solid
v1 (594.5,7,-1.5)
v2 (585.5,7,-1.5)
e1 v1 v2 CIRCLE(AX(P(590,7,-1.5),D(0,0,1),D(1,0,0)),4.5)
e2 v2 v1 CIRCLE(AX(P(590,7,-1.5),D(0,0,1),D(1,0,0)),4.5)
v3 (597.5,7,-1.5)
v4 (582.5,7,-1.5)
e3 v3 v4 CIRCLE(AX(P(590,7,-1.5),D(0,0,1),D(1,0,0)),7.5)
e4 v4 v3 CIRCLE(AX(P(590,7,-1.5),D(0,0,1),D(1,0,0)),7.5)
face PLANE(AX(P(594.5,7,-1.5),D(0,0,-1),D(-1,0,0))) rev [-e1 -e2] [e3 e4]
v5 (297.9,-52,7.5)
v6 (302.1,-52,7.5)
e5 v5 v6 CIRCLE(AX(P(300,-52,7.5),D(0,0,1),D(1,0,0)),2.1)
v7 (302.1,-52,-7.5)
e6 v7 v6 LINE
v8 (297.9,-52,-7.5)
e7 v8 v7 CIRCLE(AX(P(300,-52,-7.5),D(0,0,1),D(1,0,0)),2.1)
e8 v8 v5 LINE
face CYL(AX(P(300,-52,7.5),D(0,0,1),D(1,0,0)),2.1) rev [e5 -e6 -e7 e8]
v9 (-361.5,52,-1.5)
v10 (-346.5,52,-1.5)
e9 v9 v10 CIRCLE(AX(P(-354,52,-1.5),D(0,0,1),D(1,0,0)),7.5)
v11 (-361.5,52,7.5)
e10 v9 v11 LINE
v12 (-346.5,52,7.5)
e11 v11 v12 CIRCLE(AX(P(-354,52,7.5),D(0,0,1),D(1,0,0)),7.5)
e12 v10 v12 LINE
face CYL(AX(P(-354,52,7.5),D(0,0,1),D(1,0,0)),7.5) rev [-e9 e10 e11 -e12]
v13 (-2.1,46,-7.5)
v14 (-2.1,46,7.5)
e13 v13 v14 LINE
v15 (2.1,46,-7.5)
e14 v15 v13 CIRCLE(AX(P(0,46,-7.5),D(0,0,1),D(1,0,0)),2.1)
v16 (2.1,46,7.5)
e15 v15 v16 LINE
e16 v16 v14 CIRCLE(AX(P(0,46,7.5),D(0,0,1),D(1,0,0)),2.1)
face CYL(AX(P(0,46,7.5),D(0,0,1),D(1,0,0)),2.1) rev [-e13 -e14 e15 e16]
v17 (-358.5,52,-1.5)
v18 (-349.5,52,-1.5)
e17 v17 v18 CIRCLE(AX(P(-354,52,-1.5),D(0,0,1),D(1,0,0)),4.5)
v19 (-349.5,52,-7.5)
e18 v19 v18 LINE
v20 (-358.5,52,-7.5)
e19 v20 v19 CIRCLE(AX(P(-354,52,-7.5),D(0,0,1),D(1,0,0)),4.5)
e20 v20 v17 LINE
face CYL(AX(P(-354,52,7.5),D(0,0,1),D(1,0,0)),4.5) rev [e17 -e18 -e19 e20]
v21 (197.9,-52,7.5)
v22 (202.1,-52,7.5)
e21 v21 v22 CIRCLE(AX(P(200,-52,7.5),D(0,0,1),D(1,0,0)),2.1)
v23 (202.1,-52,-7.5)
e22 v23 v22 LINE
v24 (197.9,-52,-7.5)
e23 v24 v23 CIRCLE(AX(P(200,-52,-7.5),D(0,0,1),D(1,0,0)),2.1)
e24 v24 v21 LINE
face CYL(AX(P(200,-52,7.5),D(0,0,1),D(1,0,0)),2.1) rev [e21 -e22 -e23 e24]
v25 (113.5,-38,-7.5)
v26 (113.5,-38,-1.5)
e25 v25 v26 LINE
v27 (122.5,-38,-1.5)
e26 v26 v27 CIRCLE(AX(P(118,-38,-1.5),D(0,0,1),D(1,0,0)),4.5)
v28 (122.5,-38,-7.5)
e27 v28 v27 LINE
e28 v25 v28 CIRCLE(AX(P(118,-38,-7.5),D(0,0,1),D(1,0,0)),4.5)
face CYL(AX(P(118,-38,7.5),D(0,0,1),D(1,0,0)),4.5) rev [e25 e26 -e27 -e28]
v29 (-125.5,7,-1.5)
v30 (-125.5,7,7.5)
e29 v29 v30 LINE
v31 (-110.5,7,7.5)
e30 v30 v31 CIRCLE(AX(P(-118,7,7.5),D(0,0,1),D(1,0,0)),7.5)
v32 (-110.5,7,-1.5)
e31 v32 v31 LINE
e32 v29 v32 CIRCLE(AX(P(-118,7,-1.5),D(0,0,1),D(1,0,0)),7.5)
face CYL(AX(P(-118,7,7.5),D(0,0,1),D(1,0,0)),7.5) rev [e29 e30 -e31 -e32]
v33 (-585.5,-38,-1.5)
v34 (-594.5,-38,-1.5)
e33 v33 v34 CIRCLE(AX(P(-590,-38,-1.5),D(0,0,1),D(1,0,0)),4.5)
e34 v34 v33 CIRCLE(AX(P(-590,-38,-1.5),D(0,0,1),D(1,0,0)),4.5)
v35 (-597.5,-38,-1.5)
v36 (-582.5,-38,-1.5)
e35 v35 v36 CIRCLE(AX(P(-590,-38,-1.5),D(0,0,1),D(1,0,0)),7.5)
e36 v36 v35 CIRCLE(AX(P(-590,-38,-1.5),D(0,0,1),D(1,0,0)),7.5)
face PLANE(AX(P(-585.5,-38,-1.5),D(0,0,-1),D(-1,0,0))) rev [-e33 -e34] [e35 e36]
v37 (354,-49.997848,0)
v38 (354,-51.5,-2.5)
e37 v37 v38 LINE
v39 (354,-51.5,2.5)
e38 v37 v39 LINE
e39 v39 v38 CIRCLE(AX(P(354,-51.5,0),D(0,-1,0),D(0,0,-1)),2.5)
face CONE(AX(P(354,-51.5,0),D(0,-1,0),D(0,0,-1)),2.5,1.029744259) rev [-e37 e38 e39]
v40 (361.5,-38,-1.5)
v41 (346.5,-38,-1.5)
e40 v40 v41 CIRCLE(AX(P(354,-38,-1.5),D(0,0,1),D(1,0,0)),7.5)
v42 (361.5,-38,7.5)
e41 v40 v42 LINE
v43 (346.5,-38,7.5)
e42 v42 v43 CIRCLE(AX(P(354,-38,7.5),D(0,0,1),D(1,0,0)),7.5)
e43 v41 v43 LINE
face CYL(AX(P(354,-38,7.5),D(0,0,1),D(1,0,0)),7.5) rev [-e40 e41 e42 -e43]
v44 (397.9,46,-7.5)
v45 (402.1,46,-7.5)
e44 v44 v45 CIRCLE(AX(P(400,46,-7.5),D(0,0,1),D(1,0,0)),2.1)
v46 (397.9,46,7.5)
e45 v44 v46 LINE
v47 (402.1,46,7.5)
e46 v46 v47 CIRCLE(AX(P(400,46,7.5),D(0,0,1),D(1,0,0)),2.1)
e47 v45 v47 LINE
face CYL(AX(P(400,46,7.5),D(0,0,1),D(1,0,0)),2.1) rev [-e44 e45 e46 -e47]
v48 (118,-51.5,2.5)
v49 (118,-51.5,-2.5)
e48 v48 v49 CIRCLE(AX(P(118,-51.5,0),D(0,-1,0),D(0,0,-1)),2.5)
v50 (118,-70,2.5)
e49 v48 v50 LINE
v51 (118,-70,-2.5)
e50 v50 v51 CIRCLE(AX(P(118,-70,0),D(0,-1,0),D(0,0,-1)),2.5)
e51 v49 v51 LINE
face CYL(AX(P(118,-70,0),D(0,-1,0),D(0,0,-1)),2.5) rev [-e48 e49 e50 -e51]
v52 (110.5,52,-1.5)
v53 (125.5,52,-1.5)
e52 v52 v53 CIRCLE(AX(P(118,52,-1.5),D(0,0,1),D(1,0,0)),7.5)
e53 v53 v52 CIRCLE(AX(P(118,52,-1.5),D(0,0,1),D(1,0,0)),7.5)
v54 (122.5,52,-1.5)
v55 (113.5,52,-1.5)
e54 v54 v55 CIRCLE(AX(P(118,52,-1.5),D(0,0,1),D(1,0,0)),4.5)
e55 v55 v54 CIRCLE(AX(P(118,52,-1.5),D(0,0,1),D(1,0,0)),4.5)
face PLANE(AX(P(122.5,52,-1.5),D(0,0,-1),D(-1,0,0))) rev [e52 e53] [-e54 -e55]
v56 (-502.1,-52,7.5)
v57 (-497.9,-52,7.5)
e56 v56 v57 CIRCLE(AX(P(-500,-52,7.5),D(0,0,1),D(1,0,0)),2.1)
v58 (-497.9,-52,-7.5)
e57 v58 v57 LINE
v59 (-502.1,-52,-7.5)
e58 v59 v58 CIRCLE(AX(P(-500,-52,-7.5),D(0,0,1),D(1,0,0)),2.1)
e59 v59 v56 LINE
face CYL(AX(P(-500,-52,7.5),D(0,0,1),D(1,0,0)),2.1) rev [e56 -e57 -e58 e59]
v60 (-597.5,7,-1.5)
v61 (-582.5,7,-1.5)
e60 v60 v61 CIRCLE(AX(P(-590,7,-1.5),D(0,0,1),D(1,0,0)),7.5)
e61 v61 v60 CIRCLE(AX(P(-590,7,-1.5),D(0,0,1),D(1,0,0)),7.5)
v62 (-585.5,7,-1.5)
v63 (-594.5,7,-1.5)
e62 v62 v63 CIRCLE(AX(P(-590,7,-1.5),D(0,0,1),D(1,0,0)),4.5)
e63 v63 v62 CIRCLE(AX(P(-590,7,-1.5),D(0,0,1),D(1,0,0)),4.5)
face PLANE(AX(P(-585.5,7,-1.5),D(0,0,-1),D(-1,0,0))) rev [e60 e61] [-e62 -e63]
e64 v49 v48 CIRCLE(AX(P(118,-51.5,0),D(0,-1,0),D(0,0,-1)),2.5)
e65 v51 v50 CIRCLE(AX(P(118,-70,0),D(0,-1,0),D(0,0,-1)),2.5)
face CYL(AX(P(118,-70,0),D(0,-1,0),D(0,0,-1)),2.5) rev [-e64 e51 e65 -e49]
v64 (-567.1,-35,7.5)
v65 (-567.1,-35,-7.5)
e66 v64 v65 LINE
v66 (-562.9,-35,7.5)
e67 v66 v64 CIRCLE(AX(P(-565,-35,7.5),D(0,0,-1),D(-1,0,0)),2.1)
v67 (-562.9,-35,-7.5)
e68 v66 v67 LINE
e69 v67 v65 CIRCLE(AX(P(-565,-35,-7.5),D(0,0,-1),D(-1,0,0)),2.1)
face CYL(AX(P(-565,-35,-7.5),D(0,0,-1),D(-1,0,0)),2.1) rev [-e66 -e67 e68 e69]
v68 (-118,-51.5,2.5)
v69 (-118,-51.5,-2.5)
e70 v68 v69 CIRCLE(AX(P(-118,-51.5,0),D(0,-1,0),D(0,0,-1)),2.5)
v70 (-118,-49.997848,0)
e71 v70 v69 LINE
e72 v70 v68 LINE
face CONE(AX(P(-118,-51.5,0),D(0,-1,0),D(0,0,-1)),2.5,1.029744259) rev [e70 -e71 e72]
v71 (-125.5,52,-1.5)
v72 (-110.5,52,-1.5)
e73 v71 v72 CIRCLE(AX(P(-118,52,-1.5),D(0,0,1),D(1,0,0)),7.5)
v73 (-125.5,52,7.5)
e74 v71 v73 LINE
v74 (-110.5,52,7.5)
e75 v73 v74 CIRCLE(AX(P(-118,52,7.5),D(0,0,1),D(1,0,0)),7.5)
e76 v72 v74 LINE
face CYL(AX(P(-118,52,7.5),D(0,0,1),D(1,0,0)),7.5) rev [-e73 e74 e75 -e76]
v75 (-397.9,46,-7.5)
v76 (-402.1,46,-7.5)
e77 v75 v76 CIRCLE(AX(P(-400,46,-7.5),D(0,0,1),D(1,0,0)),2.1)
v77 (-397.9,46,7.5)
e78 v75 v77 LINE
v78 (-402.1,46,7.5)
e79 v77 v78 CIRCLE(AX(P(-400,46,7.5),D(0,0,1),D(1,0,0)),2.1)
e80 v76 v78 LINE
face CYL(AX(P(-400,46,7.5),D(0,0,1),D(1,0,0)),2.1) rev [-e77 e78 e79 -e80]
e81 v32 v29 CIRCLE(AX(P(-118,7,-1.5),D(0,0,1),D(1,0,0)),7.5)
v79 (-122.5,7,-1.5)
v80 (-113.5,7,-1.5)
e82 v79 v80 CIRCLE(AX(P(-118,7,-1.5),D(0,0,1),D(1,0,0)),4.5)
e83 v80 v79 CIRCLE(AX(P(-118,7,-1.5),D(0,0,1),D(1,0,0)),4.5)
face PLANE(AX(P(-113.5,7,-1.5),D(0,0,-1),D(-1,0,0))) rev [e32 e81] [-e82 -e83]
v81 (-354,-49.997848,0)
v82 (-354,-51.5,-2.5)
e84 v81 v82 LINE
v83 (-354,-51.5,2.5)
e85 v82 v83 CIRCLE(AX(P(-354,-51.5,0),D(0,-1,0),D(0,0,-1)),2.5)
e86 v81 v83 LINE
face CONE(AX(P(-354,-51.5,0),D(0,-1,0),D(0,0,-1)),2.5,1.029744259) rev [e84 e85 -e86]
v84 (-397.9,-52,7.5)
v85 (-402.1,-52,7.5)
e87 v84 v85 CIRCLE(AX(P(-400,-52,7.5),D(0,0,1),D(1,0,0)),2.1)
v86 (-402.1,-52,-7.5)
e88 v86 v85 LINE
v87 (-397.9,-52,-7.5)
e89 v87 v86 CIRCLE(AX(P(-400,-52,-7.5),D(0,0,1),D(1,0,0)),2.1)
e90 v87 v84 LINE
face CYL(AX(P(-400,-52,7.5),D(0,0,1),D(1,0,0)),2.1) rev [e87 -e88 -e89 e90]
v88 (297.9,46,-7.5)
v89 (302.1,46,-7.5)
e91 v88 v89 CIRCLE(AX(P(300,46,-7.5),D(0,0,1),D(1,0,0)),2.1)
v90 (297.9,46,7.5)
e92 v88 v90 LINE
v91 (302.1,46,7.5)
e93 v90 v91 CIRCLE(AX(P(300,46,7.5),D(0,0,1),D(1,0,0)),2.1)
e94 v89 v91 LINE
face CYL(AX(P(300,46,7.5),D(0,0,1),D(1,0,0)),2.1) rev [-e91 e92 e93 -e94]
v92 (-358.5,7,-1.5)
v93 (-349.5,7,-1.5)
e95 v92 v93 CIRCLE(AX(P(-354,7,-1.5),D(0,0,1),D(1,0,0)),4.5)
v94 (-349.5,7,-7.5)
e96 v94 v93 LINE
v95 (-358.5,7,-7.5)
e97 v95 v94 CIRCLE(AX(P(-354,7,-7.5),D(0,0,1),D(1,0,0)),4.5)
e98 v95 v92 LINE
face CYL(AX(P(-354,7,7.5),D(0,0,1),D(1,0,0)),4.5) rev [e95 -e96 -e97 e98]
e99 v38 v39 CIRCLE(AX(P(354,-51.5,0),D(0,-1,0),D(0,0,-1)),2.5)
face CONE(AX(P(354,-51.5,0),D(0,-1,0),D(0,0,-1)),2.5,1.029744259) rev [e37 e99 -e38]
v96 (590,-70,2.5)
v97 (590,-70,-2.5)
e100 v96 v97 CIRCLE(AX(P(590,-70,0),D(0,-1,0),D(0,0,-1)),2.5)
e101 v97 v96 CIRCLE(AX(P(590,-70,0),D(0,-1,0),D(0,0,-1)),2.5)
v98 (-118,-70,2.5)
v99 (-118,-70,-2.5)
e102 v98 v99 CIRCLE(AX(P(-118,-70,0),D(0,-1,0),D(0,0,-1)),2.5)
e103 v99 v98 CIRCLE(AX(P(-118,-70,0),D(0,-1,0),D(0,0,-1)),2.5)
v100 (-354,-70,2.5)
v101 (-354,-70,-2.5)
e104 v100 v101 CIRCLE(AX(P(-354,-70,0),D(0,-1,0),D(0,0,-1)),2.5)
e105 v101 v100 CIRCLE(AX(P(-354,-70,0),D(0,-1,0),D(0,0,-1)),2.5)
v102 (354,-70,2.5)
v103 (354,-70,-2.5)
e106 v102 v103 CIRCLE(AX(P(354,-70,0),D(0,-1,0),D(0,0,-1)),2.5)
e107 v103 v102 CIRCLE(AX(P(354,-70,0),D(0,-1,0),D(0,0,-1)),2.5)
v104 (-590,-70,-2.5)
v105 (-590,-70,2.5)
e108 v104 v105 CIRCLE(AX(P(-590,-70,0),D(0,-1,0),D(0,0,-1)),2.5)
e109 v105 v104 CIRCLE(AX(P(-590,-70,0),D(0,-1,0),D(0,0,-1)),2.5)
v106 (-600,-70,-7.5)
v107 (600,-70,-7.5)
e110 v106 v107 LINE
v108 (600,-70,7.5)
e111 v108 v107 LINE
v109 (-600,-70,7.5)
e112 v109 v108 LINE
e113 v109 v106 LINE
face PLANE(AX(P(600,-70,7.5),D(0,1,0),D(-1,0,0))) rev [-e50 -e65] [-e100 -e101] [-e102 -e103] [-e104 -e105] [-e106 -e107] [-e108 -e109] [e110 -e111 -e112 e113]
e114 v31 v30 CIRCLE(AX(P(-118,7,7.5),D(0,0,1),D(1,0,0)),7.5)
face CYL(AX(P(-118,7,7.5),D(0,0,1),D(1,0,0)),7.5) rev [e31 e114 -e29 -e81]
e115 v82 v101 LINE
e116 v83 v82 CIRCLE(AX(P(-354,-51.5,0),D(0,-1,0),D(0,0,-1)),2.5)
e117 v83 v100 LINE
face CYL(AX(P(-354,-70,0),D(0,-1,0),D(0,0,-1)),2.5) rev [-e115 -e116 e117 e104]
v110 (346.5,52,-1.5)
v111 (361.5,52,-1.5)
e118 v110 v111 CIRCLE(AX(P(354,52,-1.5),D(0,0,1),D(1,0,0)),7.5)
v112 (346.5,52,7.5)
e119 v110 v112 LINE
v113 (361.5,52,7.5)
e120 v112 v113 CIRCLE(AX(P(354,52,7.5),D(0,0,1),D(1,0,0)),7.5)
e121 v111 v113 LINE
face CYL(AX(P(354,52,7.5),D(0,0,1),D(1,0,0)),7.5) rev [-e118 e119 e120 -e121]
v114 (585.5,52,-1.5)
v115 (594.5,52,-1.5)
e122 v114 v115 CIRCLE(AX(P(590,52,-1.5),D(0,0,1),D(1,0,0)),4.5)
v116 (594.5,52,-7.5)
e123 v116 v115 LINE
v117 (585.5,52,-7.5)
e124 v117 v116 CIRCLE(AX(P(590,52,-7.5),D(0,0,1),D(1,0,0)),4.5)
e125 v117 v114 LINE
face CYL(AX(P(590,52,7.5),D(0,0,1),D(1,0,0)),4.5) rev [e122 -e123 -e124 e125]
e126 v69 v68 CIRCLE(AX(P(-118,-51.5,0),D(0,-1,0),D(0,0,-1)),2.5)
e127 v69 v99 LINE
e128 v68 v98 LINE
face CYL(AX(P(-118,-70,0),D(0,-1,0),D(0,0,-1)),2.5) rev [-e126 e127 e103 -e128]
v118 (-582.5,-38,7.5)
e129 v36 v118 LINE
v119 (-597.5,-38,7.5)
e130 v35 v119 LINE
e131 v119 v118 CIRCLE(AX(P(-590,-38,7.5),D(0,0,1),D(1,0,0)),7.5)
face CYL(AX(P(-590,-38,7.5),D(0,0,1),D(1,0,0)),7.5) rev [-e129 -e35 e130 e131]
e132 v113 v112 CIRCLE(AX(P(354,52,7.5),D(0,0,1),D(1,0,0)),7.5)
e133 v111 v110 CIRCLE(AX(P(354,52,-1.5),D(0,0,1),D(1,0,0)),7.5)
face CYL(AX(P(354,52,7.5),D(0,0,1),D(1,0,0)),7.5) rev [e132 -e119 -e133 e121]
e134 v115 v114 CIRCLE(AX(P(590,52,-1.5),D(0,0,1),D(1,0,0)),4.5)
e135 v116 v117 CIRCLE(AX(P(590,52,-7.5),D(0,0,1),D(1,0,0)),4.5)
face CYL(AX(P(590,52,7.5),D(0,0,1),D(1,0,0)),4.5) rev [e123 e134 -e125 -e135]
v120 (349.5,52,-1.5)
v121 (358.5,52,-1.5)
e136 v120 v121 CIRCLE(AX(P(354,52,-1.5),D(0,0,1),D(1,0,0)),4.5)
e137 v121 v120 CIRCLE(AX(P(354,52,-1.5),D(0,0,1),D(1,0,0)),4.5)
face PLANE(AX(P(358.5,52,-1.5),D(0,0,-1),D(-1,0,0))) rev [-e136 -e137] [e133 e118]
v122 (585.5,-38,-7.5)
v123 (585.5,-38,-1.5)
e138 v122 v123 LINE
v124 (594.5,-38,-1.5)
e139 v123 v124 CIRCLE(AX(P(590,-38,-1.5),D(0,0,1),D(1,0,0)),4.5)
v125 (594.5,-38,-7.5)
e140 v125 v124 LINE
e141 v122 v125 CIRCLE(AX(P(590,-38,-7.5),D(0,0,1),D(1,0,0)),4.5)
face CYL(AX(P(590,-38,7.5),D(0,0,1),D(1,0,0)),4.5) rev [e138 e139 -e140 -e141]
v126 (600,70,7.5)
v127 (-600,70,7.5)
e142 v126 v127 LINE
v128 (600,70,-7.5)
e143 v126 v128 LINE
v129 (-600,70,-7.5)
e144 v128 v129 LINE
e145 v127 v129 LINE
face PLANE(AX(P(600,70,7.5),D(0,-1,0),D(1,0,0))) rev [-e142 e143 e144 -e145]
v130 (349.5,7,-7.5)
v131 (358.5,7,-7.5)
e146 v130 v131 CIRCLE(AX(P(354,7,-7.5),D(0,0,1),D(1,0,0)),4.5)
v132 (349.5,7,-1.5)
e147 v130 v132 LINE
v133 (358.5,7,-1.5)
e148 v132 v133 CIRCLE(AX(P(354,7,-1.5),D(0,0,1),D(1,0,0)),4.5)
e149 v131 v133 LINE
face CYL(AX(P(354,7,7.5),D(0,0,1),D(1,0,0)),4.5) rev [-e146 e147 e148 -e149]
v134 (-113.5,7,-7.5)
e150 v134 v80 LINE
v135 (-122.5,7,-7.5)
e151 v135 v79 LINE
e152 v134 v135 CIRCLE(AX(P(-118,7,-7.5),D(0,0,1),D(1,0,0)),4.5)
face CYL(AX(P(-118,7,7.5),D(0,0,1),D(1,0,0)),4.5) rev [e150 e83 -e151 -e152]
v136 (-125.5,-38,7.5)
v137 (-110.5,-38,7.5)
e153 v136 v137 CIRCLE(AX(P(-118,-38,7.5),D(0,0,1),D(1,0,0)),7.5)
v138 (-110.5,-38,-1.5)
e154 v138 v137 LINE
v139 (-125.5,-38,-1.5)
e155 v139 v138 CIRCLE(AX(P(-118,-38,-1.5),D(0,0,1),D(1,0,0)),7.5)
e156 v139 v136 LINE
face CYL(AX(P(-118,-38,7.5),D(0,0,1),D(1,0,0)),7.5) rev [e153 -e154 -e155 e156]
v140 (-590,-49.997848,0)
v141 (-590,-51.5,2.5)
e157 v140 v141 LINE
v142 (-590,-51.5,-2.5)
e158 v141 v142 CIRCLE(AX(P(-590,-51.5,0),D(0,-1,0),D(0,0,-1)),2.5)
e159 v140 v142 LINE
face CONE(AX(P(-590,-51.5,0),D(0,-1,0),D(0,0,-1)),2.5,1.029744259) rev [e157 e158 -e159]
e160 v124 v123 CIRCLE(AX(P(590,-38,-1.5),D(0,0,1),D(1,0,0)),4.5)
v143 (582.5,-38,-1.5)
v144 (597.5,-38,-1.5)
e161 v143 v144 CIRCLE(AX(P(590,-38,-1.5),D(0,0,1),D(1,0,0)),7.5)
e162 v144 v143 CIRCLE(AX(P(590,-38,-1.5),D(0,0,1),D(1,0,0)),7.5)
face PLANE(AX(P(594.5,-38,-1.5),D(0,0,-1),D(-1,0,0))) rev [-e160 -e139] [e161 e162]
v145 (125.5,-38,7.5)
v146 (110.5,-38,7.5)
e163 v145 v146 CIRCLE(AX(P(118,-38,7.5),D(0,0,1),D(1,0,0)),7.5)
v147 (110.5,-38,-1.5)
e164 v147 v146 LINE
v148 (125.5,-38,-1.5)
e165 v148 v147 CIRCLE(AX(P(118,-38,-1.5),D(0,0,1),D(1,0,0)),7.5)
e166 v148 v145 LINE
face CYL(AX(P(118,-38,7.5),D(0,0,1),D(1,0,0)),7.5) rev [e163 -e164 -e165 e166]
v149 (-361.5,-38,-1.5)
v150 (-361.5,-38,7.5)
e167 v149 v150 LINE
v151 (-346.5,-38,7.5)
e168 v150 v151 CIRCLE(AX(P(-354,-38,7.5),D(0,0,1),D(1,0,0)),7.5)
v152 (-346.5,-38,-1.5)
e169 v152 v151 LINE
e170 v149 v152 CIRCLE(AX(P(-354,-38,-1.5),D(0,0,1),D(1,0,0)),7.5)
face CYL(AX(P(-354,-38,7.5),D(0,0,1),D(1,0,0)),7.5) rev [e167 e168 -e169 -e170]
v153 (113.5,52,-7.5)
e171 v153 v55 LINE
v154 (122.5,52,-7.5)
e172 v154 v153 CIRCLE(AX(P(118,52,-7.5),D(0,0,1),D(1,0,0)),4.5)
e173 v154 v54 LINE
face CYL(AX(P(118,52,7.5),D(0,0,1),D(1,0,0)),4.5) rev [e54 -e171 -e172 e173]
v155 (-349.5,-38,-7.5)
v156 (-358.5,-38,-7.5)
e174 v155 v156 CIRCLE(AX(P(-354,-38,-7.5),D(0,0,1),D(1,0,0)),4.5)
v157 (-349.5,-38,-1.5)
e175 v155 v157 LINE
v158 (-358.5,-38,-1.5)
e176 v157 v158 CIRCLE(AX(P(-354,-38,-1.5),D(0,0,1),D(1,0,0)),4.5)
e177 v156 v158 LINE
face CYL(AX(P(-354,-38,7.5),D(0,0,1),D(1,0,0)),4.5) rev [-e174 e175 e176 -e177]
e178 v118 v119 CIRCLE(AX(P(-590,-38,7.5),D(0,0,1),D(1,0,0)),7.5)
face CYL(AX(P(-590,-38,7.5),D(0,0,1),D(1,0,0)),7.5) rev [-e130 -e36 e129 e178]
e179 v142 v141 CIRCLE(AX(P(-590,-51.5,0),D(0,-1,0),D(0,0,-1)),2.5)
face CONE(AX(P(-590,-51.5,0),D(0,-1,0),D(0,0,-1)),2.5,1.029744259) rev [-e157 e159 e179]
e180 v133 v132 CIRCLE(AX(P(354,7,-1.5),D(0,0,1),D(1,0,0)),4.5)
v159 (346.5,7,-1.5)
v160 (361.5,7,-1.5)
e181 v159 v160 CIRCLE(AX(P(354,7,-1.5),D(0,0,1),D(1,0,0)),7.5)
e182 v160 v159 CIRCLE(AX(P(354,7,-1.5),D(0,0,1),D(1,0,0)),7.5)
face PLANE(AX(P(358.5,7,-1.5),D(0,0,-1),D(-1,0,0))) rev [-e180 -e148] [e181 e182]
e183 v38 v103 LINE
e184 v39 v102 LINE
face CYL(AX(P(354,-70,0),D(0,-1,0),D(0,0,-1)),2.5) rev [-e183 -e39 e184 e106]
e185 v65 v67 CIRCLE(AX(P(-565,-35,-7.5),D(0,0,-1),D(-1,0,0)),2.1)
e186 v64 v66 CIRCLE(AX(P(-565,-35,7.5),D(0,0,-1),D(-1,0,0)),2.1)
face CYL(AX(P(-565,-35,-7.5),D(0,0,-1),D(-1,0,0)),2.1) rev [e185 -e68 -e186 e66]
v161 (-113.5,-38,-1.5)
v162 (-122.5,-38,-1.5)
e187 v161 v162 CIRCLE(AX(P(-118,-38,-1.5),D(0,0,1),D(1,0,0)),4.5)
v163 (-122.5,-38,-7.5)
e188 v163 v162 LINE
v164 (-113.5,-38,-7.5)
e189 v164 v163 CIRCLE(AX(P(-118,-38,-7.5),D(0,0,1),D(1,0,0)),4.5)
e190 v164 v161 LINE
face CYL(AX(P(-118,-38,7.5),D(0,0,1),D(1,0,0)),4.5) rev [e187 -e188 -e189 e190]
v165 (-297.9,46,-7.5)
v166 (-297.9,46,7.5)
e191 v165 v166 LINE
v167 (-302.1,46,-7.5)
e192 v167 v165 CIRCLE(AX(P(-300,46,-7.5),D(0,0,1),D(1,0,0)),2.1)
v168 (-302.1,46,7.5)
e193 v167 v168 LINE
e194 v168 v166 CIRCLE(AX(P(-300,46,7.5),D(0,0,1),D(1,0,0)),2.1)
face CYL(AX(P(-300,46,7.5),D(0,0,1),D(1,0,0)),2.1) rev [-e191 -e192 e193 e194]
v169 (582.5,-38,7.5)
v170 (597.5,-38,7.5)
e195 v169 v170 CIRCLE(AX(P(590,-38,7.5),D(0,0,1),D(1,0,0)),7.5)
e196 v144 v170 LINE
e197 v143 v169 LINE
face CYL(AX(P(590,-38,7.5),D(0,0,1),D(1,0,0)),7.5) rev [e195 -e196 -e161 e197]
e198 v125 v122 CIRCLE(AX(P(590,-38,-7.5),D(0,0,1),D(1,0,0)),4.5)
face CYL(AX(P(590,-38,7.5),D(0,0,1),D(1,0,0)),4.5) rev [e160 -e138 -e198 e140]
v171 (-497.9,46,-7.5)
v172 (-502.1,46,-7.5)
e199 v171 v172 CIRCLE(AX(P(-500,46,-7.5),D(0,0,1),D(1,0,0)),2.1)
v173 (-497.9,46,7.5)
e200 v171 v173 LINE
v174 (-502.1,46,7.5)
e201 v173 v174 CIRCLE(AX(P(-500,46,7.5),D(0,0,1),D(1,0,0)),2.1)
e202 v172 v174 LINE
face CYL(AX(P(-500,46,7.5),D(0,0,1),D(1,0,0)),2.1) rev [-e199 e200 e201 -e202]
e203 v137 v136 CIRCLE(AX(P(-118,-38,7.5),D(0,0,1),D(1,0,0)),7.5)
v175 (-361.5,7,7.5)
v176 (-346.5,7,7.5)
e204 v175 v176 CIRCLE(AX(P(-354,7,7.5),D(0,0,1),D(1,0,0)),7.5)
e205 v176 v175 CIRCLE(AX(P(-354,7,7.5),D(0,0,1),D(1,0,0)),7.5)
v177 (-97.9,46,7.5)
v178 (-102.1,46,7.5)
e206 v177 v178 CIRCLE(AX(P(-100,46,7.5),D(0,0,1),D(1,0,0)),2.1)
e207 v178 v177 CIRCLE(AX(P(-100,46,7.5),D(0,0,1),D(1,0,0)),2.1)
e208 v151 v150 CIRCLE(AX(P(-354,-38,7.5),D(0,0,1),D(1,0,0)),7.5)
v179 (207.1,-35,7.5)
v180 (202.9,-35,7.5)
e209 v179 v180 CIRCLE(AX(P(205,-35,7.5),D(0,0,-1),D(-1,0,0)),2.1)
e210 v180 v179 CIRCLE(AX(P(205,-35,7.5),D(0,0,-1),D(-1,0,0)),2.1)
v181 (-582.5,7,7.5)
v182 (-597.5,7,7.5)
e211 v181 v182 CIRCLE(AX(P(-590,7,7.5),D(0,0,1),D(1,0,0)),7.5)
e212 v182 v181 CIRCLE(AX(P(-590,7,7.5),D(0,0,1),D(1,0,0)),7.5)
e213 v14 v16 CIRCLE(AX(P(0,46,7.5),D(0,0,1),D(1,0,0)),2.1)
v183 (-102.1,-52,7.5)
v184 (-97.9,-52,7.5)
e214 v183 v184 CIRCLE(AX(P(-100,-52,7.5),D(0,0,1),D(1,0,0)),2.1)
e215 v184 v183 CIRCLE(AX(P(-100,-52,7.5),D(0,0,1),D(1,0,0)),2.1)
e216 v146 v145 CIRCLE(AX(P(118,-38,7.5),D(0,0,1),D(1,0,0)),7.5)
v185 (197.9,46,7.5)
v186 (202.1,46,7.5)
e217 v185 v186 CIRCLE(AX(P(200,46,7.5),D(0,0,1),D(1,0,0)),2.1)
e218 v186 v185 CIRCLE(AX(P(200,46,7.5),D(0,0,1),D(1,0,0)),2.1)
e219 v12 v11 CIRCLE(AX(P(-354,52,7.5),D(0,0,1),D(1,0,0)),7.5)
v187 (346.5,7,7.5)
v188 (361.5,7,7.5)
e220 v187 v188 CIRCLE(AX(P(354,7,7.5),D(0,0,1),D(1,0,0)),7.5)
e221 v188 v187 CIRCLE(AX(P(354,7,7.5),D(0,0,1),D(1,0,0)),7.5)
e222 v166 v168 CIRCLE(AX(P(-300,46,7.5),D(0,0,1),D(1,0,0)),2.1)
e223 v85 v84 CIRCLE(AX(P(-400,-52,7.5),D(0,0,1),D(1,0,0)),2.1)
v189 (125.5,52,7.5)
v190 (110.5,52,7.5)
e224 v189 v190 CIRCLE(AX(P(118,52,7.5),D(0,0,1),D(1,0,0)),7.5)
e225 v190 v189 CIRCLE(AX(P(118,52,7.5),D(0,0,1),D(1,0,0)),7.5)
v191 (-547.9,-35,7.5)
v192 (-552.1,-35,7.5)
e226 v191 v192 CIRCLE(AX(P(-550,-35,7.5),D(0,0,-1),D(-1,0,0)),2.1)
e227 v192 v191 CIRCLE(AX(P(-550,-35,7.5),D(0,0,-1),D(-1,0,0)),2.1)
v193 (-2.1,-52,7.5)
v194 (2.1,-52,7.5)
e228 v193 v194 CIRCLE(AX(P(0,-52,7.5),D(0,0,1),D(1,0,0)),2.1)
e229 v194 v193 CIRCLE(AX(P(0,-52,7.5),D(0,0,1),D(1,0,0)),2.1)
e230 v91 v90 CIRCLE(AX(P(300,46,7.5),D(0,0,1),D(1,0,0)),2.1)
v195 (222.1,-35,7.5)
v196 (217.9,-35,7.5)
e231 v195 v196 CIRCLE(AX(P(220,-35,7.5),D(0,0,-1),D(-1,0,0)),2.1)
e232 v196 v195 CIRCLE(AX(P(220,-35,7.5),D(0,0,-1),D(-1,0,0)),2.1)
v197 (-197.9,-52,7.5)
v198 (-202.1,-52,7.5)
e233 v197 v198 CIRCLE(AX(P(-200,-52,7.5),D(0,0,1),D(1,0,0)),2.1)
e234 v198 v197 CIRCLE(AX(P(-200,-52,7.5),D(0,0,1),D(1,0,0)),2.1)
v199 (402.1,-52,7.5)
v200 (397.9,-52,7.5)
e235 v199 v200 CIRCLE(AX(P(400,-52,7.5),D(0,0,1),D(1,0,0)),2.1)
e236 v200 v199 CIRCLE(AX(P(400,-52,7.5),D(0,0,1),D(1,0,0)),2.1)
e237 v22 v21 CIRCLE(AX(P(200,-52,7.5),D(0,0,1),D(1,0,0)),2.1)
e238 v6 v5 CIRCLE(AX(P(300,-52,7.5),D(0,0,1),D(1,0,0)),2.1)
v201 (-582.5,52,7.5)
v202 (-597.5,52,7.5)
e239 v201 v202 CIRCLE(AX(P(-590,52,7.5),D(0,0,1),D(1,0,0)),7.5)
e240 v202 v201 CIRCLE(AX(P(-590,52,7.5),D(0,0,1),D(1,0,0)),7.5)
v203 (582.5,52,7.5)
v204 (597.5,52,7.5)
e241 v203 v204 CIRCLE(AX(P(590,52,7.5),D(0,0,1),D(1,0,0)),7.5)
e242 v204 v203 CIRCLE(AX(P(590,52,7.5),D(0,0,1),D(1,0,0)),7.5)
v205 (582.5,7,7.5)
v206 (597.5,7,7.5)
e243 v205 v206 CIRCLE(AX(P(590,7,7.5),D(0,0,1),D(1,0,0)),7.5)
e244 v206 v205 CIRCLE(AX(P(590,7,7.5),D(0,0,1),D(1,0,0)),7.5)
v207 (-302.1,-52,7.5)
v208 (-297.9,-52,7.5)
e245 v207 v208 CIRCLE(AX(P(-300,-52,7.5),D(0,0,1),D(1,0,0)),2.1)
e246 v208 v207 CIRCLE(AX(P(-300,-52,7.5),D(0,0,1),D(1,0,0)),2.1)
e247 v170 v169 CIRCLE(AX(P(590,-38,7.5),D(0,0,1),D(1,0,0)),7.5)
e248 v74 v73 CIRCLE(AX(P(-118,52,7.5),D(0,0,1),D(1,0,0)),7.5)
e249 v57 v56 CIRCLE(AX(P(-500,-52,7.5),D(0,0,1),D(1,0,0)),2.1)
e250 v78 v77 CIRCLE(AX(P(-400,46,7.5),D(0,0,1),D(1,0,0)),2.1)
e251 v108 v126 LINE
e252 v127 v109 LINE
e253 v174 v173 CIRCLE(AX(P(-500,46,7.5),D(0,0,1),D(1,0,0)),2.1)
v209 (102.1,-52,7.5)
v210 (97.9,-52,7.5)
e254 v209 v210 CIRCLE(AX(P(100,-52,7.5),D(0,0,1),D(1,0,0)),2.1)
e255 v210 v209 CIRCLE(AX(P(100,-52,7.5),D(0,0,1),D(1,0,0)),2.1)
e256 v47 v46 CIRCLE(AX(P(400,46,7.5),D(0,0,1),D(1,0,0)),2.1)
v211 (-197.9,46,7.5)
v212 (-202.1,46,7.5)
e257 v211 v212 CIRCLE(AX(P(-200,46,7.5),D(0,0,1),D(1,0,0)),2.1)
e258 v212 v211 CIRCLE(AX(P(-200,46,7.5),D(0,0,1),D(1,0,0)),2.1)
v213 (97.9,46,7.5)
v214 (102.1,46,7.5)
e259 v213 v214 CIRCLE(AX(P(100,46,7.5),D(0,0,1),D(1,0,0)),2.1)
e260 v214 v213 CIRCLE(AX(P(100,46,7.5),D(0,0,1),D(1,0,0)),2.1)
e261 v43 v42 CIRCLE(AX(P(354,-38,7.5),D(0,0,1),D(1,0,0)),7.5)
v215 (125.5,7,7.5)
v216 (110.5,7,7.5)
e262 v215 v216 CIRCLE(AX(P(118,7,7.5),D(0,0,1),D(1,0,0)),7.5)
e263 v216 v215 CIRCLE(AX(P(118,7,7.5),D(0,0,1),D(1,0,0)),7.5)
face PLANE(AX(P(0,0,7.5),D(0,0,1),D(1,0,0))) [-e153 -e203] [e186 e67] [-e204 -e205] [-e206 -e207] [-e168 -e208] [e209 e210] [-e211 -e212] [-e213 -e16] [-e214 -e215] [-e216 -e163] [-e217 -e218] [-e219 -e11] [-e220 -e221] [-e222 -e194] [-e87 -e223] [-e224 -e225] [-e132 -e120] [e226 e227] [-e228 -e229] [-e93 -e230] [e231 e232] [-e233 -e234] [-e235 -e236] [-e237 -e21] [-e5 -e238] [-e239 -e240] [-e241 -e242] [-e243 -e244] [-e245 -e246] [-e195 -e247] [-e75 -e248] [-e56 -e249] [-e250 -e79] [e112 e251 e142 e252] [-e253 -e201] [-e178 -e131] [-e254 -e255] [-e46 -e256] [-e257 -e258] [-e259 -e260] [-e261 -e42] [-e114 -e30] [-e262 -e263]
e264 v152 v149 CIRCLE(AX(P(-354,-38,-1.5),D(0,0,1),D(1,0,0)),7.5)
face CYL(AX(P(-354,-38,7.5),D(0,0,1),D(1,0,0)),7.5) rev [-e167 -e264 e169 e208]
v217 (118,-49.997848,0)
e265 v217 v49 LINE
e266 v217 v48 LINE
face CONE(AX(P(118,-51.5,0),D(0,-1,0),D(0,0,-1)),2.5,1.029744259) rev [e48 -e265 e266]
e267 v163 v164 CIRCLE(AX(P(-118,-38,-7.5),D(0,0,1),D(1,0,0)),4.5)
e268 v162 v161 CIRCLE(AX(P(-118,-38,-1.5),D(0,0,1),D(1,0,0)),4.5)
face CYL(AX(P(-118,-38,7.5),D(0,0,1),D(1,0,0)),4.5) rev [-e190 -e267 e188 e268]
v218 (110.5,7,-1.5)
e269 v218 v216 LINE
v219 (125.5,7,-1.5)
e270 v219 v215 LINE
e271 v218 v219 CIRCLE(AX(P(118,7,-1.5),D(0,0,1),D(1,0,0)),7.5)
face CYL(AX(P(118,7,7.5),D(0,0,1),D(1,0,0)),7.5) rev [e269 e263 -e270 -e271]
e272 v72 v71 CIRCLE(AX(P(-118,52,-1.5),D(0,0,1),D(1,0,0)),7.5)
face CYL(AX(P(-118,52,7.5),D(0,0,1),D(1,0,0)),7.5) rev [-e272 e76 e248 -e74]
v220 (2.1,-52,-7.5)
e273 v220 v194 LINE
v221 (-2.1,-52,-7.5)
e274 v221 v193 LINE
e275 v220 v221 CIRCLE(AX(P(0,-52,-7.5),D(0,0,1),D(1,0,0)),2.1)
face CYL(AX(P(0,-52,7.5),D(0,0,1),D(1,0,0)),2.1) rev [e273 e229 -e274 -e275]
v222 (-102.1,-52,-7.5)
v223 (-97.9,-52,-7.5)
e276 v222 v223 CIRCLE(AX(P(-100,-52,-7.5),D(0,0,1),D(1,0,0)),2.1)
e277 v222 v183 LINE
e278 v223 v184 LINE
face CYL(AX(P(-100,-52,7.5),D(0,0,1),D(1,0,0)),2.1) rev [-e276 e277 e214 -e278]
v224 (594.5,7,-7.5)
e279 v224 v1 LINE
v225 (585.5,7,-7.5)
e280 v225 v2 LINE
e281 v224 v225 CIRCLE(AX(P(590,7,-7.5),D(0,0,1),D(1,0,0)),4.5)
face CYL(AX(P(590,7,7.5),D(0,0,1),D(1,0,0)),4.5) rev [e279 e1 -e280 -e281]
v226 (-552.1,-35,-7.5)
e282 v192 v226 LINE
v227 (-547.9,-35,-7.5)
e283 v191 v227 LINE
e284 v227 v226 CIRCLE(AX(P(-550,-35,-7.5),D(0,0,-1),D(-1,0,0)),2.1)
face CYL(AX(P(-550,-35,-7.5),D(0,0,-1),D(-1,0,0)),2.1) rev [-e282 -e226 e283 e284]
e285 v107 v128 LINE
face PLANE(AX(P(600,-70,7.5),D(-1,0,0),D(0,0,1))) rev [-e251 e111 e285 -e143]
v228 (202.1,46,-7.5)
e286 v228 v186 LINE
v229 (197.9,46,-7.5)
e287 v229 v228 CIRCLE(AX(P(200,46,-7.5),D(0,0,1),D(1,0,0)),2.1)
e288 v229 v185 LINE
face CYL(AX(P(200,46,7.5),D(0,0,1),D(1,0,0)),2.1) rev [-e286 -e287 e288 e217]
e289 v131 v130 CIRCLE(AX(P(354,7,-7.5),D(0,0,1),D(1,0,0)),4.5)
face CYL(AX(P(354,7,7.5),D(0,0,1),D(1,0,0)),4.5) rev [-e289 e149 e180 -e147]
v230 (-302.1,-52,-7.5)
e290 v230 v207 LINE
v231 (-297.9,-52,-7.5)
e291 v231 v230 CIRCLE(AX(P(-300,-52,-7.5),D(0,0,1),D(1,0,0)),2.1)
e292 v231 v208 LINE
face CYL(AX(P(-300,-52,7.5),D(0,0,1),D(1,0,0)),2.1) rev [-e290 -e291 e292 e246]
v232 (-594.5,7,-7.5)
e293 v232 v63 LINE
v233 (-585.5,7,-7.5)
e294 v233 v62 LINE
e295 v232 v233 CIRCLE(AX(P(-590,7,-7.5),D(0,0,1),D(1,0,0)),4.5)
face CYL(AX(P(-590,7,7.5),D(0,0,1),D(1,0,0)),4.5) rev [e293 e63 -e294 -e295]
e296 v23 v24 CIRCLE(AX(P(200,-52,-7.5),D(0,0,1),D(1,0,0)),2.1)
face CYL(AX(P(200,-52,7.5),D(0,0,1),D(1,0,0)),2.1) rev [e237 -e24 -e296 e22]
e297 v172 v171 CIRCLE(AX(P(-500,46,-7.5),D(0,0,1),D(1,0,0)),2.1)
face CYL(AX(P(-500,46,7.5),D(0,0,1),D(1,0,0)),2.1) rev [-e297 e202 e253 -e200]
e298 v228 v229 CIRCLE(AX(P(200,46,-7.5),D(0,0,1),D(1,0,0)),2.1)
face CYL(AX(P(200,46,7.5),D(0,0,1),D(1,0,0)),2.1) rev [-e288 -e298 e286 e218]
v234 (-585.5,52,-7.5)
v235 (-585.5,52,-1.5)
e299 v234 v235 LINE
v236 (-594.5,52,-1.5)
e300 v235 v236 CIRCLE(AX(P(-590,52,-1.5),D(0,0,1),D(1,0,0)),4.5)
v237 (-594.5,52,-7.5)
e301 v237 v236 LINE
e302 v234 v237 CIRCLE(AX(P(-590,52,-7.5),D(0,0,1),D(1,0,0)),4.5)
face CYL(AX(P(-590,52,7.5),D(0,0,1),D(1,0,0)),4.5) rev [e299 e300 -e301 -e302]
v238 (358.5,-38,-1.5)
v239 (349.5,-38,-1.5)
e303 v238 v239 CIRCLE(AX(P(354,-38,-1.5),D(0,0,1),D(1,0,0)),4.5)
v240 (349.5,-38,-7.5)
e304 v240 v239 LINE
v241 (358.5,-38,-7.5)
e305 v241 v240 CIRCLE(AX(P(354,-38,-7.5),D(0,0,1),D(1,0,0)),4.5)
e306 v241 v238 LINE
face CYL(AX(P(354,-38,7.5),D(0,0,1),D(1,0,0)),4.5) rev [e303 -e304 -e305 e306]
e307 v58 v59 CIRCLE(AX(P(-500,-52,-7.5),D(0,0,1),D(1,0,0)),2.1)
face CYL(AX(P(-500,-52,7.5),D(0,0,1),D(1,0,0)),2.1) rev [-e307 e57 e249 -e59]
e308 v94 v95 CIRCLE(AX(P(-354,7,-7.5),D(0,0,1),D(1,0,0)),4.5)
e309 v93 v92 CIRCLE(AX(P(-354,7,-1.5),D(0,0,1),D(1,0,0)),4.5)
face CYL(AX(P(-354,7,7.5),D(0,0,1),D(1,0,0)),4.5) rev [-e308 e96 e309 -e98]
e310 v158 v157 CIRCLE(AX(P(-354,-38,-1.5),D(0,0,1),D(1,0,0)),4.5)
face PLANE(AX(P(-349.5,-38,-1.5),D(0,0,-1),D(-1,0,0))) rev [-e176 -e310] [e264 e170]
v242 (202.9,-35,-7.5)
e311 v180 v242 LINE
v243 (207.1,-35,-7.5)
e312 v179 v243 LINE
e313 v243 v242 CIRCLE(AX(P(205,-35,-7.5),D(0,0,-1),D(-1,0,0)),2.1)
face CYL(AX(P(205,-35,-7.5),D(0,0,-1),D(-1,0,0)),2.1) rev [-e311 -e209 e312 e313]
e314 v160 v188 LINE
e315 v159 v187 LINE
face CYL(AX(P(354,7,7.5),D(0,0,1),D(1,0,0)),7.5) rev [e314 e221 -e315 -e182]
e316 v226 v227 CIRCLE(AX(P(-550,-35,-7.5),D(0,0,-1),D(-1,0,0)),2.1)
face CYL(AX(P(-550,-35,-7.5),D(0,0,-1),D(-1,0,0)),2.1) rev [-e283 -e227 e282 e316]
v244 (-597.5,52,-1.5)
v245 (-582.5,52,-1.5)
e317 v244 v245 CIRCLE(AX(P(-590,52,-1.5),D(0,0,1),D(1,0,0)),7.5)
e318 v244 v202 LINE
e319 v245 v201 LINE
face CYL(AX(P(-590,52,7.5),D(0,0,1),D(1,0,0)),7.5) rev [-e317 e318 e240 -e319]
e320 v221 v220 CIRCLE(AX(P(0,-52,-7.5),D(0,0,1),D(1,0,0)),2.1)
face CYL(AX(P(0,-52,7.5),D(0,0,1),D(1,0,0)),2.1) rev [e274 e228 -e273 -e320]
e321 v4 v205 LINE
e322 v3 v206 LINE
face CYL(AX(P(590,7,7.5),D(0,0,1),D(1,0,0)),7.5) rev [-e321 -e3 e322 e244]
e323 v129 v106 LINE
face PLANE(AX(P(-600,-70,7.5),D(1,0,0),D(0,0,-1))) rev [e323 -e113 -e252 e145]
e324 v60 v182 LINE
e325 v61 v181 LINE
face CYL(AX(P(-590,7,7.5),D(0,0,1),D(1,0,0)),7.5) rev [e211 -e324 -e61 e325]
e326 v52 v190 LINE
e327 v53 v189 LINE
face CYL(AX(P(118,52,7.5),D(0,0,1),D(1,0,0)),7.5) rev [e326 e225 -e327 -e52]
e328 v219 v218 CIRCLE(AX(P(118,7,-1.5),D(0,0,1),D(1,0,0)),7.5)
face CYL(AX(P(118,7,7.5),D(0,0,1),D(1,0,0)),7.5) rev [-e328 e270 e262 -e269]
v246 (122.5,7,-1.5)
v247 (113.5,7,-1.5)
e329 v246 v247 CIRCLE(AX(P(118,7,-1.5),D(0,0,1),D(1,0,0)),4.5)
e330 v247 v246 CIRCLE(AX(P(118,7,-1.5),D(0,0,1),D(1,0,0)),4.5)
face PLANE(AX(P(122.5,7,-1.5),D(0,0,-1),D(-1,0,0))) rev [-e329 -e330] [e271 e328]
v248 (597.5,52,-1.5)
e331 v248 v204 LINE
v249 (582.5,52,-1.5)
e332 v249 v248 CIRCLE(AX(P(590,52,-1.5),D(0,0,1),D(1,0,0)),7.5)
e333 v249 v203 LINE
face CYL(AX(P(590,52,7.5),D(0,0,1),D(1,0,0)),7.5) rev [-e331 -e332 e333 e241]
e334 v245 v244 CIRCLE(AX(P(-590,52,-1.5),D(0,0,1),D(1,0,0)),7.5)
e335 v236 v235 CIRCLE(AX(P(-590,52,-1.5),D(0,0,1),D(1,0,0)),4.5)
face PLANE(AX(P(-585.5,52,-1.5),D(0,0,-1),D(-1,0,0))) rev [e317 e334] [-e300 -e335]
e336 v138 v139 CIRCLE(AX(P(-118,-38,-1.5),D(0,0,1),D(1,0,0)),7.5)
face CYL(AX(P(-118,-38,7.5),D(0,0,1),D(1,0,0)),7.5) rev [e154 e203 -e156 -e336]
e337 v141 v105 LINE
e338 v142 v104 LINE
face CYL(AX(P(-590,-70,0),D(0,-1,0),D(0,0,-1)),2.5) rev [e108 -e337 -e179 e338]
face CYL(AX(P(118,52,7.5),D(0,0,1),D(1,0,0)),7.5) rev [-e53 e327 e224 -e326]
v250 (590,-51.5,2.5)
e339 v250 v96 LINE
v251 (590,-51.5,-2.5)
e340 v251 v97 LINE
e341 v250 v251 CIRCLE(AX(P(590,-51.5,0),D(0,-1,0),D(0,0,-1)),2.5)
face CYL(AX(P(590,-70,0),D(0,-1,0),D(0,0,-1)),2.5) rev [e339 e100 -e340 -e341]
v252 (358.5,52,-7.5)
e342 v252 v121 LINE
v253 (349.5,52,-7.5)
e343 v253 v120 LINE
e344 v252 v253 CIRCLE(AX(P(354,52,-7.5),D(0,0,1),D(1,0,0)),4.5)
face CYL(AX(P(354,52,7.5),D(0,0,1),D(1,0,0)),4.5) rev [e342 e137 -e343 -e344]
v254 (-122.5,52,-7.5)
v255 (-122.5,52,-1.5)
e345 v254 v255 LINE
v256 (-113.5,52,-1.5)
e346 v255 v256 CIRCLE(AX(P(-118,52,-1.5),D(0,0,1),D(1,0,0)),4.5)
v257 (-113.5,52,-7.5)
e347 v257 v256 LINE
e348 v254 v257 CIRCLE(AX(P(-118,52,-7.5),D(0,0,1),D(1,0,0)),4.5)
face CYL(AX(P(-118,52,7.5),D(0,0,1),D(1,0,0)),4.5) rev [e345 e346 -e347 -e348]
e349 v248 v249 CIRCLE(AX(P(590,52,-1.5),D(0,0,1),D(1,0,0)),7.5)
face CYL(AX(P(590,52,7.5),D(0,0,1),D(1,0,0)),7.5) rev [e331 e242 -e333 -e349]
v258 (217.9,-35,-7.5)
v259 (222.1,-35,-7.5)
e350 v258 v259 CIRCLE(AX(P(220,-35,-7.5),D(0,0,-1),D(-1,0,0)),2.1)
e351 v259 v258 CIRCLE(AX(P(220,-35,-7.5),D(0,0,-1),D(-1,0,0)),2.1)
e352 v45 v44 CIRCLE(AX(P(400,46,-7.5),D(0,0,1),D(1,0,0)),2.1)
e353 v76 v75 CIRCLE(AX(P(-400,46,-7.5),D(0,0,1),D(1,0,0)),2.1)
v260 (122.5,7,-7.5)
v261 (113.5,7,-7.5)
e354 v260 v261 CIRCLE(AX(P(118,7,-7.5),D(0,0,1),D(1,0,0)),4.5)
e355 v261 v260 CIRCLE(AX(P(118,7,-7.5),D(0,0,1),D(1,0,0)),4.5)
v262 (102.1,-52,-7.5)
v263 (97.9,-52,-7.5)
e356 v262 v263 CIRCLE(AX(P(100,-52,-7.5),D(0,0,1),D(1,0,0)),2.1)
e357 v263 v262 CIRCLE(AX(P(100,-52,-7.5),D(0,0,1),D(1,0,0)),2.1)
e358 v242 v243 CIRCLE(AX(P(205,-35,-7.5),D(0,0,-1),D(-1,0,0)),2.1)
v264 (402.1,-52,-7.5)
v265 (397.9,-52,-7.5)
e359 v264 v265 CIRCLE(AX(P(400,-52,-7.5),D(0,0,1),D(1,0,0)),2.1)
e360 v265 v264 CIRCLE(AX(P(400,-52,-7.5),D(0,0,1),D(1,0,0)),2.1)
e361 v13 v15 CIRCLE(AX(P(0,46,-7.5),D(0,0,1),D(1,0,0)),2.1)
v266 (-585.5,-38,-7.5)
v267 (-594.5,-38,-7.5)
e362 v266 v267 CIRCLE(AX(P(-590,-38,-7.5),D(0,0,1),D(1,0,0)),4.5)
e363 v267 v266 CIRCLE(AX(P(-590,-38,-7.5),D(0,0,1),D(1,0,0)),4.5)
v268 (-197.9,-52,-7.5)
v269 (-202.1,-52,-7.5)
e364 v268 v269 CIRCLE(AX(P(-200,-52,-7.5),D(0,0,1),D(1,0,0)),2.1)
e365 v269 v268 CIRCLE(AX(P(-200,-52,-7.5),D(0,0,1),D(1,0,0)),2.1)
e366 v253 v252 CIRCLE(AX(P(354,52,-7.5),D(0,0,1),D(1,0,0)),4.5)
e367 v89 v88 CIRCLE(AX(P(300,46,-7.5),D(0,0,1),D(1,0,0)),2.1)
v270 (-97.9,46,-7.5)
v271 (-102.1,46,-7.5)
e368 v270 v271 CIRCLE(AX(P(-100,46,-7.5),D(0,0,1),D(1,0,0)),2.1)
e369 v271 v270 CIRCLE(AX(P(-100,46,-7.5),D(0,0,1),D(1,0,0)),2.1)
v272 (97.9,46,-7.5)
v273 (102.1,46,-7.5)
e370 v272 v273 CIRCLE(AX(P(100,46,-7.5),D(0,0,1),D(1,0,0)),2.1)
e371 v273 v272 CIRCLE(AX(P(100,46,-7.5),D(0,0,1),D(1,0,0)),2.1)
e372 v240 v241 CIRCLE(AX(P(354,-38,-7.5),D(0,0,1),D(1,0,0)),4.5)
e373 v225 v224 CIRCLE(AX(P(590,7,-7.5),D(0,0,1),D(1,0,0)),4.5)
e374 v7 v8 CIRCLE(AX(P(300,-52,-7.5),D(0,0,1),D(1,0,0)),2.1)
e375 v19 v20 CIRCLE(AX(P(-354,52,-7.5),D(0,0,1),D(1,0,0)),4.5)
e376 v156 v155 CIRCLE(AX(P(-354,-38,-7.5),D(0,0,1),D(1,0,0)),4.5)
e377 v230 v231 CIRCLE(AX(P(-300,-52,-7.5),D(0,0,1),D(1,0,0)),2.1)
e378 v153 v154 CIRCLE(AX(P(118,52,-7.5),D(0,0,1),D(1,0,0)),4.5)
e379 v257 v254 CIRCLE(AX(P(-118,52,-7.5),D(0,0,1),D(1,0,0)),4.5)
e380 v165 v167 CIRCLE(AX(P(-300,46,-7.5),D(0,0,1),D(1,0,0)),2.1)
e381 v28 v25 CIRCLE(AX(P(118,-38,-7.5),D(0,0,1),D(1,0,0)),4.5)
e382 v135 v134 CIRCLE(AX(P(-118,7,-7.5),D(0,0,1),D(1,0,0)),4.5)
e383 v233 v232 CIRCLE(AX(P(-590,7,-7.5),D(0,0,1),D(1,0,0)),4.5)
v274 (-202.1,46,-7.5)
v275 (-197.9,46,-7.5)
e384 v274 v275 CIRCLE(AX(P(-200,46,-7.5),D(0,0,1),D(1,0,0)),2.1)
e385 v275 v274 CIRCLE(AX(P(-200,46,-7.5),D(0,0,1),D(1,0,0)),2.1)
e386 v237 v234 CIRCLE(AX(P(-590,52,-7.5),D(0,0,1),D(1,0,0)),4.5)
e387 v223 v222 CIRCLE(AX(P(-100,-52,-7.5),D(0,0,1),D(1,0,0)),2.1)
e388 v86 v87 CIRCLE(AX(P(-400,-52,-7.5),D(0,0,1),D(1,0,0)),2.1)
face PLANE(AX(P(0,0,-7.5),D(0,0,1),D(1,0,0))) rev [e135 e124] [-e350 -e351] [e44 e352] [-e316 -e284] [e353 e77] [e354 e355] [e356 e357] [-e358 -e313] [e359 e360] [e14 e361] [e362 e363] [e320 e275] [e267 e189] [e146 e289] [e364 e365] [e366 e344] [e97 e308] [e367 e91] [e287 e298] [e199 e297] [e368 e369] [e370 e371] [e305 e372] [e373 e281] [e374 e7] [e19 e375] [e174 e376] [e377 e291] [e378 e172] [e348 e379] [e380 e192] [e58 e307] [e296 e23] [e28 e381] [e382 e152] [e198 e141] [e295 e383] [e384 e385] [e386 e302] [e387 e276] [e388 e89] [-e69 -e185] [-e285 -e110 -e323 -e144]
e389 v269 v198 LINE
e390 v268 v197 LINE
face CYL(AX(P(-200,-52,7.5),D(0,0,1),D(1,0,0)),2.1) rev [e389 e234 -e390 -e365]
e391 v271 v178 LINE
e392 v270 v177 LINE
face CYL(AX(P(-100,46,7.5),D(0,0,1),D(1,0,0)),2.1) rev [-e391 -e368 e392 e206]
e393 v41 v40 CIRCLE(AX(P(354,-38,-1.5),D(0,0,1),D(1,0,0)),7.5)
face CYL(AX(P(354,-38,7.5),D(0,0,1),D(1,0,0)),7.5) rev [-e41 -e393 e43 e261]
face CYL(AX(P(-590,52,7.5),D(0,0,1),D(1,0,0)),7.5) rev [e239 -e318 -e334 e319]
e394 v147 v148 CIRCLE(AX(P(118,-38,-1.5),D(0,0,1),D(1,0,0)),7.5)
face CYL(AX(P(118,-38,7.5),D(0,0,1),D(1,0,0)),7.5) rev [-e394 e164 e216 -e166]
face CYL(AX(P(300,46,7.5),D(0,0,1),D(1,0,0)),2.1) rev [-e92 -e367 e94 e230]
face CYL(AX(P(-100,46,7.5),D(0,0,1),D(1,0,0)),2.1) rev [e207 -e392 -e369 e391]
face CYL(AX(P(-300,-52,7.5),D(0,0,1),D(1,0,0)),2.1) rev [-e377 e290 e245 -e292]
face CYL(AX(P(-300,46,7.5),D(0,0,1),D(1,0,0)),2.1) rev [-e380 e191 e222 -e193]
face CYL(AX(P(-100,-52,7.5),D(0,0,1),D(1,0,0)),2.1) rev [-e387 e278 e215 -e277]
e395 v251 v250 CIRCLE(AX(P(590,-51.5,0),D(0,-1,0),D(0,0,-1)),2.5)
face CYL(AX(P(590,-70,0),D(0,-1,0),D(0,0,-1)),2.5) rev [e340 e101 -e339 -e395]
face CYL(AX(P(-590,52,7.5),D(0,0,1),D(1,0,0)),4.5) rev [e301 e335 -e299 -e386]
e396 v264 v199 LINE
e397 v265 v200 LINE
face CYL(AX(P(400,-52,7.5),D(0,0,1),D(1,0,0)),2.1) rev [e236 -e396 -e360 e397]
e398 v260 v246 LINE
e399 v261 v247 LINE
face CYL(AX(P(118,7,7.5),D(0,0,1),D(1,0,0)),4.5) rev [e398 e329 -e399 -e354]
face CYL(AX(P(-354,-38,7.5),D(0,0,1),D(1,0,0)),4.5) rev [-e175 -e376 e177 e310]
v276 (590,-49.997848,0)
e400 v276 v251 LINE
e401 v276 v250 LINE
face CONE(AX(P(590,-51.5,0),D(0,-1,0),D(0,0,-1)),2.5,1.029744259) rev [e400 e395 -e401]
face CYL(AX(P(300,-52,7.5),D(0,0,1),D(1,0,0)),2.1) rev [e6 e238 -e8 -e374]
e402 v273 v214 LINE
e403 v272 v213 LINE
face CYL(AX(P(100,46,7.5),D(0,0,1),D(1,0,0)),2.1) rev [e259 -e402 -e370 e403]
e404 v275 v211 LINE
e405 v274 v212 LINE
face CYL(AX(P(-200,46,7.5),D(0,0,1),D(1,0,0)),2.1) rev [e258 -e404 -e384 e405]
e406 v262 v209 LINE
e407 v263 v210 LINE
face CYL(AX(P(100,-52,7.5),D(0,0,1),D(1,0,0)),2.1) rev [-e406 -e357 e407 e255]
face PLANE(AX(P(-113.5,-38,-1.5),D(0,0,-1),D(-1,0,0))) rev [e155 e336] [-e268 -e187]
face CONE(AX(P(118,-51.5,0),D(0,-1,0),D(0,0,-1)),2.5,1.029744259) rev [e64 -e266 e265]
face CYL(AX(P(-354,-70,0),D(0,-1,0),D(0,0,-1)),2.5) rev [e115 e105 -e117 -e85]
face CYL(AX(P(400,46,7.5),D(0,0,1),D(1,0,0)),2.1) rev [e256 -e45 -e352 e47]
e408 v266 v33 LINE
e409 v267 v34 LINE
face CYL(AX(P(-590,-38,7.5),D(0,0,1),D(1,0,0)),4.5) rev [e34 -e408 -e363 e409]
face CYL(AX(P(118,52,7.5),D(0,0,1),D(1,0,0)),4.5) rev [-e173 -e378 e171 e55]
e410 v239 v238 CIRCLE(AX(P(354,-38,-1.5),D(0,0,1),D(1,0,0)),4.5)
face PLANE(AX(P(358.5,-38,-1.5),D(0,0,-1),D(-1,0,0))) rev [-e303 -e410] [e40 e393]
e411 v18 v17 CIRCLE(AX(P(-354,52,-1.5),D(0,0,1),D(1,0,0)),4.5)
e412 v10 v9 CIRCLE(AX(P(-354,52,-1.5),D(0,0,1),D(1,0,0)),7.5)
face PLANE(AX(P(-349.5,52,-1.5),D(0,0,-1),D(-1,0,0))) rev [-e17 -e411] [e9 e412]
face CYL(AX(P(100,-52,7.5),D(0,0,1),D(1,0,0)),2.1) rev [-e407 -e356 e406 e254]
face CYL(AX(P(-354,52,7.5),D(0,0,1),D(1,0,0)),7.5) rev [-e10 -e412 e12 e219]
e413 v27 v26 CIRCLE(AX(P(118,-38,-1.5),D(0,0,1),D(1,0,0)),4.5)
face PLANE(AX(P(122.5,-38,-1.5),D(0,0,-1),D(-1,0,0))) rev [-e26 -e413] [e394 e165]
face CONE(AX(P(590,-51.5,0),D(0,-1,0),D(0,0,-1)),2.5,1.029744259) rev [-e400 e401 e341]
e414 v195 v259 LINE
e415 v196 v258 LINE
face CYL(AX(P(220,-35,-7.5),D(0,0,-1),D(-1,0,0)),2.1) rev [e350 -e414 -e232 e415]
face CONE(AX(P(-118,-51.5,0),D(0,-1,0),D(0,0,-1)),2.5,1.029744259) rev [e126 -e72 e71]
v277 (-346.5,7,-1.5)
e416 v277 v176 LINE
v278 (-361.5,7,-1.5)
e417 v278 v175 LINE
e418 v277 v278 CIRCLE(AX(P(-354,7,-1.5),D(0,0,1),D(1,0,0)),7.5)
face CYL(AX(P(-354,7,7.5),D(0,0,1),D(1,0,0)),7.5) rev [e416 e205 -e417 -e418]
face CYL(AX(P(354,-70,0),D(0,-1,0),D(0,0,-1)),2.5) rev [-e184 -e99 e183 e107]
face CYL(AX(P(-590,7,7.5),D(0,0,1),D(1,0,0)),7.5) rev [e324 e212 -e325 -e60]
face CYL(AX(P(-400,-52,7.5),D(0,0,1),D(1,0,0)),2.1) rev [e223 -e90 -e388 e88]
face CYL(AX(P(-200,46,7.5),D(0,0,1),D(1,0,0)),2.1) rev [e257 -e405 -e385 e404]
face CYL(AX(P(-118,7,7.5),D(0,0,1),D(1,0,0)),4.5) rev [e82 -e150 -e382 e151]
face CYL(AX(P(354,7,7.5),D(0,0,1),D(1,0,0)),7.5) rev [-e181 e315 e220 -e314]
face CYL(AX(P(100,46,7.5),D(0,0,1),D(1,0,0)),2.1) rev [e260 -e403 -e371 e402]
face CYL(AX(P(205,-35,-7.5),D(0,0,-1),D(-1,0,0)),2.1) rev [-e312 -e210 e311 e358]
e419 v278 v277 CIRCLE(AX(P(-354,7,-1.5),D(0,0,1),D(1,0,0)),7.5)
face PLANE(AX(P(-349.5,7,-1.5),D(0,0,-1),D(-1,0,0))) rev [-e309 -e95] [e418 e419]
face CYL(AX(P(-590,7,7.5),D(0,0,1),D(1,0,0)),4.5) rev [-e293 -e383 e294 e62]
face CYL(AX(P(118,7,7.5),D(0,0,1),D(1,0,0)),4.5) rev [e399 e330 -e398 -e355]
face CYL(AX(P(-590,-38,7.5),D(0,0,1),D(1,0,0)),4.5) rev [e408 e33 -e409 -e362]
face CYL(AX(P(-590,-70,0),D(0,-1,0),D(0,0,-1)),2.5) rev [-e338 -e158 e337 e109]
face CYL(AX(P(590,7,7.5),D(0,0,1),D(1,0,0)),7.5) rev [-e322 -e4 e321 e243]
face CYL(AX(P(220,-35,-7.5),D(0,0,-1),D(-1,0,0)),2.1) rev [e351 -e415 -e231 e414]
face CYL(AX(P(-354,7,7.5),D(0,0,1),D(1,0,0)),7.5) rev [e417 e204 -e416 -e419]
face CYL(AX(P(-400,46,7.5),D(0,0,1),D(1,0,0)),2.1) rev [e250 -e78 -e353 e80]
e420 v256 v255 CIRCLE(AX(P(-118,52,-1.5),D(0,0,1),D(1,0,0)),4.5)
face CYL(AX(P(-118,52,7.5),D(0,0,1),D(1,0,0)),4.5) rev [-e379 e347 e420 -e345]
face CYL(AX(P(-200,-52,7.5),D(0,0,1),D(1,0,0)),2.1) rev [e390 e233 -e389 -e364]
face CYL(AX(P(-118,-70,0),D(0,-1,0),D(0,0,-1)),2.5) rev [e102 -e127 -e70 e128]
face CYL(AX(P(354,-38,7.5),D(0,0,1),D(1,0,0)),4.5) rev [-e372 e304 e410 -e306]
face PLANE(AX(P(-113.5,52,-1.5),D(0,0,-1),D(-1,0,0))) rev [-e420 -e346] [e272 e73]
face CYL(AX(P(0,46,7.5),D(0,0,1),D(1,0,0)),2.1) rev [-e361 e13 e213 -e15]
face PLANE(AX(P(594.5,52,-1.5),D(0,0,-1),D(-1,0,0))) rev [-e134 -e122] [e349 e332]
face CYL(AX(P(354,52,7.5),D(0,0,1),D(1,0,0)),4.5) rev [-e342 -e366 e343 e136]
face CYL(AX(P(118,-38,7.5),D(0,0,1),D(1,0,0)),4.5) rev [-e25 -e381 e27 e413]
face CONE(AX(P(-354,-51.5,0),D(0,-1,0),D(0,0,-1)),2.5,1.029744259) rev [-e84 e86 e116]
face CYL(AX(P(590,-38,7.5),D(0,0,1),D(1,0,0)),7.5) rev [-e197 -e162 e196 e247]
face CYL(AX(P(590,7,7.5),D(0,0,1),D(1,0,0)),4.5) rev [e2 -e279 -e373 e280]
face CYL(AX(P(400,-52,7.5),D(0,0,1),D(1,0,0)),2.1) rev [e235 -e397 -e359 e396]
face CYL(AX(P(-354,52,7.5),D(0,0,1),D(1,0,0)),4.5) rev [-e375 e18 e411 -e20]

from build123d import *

# Parameters (mm, degrees)
SKETCH_1_W                = 1200
SKETCH_1_H                = 140
EXTRUDE_1_DEPTH           = 7.5
PATTERN_LINEAR_1_COUNT    = 6
PATTERN_LINEAR_1_PITCH    = 236
HOLE_WIZARD_1_D           = 9
HOLE_WIZARD_1_CBORE_D     = 15
HOLE_WIZARD_1_CBORE_DEPTH = 9
PATTERN_LINEAR_2_COUNT    = 6
PATTERN_LINEAR_2_PITCH    = 236
HOLE_WIZARD_M5_1_D        = 4.2
PATTERN_LINEAR_3_COUNT    = 2
PATTERN_LINEAR_3_PITCH    = 770
HOLE_WIZARD_M5_2_D        = 4.2
PATTERN_LINEAR_4_COUNT    = 10
PATTERN_LINEAR_4_PITCH    = 100


with BuildPart() as part:
    # 草图1 → 凸台-拉伸1 (new, symmetric)
    with BuildSketch(Plane.XY):
        Rectangle(SKETCH_1_W, SKETCH_1_H)
    extrude(amount=EXTRUDE_1_DEPTH, both=True)

    # 草图3 → M6 螺纹孔1 (revolve, cut)
    with BuildSketch(Plane(origin=(-590, -70, 0), x_dir=(0, 0, -1), z_dir=(1, 0, 0))):
        Polygon((0, 0), (0, 20.002151548), (2.5, 18.5), (2.5, 0), align=None)
    hole_wizard_m6_1 = revolve(axis=Axis((-590, -76.35, 0), (0, 1, 0)), mode=Mode.SUBTRACT)

    # 阵列(线性)1: M6 螺纹孔1 ×6
    with Locations(*[(i * PATTERN_LINEAR_1_PITCH, 0, 0) for i in range(1, PATTERN_LINEAR_1_COUNT)]):
        add(hole_wizard_m6_1, mode=Mode.SUBTRACT)

    # 打孔尺寸(%根据)内六角圆柱头螺钉的类型1 (through all)
    with Locations(Plane.XY.offset(7.5)):
        with Locations((-590, 52), (-590, 7), (-590, -38)):
            hole_wizard_1 = CounterBoreHole(HOLE_WIZARD_1_D / 2, HOLE_WIZARD_1_CBORE_D / 2, HOLE_WIZARD_1_CBORE_DEPTH)

    # 阵列(线性)2: 打孔尺寸(%根据)内六角圆柱头螺钉的类型1 ×6
    with Locations(*[(i * PATTERN_LINEAR_2_PITCH, 0, 0) for i in range(1, PATTERN_LINEAR_2_COUNT)]):
        add(hole_wizard_1, mode=Mode.SUBTRACT)

    # M5 螺纹孔1 (through all)
    with Locations(Plane(origin=(0, 0, -7.5), x_dir=(-1, 0, 0), z_dir=(0, 0, -1))):
        with Locations((550, -35), (565, -35)):
            hole_wizard_m5_1 = Hole(HOLE_WIZARD_M5_1_D / 2)

    # 阵列(线性)3: M5 螺纹孔1 ×2
    with Locations(*[(i * PATTERN_LINEAR_3_PITCH, 0, 0) for i in range(1, PATTERN_LINEAR_3_COUNT)]):
        add(hole_wizard_m5_1, mode=Mode.SUBTRACT)

    # M5 螺纹孔2 (through all)
    with Locations(Plane.XY.offset(7.5)):
        with Locations((-500, 46), (-500, -52)):
            hole_wizard_m5_2 = Hole(HOLE_WIZARD_M5_2_D / 2)

    # 阵列(线性)4: M5 螺纹孔2 ×10
    with Locations(*[(i * PATTERN_LINEAR_4_PITCH, 0, 0) for i in range(1, PATTERN_LINEAR_4_COUNT)]):
        add(hole_wizard_m5_2, mode=Mode.SUBTRACT)


solid = part.part
